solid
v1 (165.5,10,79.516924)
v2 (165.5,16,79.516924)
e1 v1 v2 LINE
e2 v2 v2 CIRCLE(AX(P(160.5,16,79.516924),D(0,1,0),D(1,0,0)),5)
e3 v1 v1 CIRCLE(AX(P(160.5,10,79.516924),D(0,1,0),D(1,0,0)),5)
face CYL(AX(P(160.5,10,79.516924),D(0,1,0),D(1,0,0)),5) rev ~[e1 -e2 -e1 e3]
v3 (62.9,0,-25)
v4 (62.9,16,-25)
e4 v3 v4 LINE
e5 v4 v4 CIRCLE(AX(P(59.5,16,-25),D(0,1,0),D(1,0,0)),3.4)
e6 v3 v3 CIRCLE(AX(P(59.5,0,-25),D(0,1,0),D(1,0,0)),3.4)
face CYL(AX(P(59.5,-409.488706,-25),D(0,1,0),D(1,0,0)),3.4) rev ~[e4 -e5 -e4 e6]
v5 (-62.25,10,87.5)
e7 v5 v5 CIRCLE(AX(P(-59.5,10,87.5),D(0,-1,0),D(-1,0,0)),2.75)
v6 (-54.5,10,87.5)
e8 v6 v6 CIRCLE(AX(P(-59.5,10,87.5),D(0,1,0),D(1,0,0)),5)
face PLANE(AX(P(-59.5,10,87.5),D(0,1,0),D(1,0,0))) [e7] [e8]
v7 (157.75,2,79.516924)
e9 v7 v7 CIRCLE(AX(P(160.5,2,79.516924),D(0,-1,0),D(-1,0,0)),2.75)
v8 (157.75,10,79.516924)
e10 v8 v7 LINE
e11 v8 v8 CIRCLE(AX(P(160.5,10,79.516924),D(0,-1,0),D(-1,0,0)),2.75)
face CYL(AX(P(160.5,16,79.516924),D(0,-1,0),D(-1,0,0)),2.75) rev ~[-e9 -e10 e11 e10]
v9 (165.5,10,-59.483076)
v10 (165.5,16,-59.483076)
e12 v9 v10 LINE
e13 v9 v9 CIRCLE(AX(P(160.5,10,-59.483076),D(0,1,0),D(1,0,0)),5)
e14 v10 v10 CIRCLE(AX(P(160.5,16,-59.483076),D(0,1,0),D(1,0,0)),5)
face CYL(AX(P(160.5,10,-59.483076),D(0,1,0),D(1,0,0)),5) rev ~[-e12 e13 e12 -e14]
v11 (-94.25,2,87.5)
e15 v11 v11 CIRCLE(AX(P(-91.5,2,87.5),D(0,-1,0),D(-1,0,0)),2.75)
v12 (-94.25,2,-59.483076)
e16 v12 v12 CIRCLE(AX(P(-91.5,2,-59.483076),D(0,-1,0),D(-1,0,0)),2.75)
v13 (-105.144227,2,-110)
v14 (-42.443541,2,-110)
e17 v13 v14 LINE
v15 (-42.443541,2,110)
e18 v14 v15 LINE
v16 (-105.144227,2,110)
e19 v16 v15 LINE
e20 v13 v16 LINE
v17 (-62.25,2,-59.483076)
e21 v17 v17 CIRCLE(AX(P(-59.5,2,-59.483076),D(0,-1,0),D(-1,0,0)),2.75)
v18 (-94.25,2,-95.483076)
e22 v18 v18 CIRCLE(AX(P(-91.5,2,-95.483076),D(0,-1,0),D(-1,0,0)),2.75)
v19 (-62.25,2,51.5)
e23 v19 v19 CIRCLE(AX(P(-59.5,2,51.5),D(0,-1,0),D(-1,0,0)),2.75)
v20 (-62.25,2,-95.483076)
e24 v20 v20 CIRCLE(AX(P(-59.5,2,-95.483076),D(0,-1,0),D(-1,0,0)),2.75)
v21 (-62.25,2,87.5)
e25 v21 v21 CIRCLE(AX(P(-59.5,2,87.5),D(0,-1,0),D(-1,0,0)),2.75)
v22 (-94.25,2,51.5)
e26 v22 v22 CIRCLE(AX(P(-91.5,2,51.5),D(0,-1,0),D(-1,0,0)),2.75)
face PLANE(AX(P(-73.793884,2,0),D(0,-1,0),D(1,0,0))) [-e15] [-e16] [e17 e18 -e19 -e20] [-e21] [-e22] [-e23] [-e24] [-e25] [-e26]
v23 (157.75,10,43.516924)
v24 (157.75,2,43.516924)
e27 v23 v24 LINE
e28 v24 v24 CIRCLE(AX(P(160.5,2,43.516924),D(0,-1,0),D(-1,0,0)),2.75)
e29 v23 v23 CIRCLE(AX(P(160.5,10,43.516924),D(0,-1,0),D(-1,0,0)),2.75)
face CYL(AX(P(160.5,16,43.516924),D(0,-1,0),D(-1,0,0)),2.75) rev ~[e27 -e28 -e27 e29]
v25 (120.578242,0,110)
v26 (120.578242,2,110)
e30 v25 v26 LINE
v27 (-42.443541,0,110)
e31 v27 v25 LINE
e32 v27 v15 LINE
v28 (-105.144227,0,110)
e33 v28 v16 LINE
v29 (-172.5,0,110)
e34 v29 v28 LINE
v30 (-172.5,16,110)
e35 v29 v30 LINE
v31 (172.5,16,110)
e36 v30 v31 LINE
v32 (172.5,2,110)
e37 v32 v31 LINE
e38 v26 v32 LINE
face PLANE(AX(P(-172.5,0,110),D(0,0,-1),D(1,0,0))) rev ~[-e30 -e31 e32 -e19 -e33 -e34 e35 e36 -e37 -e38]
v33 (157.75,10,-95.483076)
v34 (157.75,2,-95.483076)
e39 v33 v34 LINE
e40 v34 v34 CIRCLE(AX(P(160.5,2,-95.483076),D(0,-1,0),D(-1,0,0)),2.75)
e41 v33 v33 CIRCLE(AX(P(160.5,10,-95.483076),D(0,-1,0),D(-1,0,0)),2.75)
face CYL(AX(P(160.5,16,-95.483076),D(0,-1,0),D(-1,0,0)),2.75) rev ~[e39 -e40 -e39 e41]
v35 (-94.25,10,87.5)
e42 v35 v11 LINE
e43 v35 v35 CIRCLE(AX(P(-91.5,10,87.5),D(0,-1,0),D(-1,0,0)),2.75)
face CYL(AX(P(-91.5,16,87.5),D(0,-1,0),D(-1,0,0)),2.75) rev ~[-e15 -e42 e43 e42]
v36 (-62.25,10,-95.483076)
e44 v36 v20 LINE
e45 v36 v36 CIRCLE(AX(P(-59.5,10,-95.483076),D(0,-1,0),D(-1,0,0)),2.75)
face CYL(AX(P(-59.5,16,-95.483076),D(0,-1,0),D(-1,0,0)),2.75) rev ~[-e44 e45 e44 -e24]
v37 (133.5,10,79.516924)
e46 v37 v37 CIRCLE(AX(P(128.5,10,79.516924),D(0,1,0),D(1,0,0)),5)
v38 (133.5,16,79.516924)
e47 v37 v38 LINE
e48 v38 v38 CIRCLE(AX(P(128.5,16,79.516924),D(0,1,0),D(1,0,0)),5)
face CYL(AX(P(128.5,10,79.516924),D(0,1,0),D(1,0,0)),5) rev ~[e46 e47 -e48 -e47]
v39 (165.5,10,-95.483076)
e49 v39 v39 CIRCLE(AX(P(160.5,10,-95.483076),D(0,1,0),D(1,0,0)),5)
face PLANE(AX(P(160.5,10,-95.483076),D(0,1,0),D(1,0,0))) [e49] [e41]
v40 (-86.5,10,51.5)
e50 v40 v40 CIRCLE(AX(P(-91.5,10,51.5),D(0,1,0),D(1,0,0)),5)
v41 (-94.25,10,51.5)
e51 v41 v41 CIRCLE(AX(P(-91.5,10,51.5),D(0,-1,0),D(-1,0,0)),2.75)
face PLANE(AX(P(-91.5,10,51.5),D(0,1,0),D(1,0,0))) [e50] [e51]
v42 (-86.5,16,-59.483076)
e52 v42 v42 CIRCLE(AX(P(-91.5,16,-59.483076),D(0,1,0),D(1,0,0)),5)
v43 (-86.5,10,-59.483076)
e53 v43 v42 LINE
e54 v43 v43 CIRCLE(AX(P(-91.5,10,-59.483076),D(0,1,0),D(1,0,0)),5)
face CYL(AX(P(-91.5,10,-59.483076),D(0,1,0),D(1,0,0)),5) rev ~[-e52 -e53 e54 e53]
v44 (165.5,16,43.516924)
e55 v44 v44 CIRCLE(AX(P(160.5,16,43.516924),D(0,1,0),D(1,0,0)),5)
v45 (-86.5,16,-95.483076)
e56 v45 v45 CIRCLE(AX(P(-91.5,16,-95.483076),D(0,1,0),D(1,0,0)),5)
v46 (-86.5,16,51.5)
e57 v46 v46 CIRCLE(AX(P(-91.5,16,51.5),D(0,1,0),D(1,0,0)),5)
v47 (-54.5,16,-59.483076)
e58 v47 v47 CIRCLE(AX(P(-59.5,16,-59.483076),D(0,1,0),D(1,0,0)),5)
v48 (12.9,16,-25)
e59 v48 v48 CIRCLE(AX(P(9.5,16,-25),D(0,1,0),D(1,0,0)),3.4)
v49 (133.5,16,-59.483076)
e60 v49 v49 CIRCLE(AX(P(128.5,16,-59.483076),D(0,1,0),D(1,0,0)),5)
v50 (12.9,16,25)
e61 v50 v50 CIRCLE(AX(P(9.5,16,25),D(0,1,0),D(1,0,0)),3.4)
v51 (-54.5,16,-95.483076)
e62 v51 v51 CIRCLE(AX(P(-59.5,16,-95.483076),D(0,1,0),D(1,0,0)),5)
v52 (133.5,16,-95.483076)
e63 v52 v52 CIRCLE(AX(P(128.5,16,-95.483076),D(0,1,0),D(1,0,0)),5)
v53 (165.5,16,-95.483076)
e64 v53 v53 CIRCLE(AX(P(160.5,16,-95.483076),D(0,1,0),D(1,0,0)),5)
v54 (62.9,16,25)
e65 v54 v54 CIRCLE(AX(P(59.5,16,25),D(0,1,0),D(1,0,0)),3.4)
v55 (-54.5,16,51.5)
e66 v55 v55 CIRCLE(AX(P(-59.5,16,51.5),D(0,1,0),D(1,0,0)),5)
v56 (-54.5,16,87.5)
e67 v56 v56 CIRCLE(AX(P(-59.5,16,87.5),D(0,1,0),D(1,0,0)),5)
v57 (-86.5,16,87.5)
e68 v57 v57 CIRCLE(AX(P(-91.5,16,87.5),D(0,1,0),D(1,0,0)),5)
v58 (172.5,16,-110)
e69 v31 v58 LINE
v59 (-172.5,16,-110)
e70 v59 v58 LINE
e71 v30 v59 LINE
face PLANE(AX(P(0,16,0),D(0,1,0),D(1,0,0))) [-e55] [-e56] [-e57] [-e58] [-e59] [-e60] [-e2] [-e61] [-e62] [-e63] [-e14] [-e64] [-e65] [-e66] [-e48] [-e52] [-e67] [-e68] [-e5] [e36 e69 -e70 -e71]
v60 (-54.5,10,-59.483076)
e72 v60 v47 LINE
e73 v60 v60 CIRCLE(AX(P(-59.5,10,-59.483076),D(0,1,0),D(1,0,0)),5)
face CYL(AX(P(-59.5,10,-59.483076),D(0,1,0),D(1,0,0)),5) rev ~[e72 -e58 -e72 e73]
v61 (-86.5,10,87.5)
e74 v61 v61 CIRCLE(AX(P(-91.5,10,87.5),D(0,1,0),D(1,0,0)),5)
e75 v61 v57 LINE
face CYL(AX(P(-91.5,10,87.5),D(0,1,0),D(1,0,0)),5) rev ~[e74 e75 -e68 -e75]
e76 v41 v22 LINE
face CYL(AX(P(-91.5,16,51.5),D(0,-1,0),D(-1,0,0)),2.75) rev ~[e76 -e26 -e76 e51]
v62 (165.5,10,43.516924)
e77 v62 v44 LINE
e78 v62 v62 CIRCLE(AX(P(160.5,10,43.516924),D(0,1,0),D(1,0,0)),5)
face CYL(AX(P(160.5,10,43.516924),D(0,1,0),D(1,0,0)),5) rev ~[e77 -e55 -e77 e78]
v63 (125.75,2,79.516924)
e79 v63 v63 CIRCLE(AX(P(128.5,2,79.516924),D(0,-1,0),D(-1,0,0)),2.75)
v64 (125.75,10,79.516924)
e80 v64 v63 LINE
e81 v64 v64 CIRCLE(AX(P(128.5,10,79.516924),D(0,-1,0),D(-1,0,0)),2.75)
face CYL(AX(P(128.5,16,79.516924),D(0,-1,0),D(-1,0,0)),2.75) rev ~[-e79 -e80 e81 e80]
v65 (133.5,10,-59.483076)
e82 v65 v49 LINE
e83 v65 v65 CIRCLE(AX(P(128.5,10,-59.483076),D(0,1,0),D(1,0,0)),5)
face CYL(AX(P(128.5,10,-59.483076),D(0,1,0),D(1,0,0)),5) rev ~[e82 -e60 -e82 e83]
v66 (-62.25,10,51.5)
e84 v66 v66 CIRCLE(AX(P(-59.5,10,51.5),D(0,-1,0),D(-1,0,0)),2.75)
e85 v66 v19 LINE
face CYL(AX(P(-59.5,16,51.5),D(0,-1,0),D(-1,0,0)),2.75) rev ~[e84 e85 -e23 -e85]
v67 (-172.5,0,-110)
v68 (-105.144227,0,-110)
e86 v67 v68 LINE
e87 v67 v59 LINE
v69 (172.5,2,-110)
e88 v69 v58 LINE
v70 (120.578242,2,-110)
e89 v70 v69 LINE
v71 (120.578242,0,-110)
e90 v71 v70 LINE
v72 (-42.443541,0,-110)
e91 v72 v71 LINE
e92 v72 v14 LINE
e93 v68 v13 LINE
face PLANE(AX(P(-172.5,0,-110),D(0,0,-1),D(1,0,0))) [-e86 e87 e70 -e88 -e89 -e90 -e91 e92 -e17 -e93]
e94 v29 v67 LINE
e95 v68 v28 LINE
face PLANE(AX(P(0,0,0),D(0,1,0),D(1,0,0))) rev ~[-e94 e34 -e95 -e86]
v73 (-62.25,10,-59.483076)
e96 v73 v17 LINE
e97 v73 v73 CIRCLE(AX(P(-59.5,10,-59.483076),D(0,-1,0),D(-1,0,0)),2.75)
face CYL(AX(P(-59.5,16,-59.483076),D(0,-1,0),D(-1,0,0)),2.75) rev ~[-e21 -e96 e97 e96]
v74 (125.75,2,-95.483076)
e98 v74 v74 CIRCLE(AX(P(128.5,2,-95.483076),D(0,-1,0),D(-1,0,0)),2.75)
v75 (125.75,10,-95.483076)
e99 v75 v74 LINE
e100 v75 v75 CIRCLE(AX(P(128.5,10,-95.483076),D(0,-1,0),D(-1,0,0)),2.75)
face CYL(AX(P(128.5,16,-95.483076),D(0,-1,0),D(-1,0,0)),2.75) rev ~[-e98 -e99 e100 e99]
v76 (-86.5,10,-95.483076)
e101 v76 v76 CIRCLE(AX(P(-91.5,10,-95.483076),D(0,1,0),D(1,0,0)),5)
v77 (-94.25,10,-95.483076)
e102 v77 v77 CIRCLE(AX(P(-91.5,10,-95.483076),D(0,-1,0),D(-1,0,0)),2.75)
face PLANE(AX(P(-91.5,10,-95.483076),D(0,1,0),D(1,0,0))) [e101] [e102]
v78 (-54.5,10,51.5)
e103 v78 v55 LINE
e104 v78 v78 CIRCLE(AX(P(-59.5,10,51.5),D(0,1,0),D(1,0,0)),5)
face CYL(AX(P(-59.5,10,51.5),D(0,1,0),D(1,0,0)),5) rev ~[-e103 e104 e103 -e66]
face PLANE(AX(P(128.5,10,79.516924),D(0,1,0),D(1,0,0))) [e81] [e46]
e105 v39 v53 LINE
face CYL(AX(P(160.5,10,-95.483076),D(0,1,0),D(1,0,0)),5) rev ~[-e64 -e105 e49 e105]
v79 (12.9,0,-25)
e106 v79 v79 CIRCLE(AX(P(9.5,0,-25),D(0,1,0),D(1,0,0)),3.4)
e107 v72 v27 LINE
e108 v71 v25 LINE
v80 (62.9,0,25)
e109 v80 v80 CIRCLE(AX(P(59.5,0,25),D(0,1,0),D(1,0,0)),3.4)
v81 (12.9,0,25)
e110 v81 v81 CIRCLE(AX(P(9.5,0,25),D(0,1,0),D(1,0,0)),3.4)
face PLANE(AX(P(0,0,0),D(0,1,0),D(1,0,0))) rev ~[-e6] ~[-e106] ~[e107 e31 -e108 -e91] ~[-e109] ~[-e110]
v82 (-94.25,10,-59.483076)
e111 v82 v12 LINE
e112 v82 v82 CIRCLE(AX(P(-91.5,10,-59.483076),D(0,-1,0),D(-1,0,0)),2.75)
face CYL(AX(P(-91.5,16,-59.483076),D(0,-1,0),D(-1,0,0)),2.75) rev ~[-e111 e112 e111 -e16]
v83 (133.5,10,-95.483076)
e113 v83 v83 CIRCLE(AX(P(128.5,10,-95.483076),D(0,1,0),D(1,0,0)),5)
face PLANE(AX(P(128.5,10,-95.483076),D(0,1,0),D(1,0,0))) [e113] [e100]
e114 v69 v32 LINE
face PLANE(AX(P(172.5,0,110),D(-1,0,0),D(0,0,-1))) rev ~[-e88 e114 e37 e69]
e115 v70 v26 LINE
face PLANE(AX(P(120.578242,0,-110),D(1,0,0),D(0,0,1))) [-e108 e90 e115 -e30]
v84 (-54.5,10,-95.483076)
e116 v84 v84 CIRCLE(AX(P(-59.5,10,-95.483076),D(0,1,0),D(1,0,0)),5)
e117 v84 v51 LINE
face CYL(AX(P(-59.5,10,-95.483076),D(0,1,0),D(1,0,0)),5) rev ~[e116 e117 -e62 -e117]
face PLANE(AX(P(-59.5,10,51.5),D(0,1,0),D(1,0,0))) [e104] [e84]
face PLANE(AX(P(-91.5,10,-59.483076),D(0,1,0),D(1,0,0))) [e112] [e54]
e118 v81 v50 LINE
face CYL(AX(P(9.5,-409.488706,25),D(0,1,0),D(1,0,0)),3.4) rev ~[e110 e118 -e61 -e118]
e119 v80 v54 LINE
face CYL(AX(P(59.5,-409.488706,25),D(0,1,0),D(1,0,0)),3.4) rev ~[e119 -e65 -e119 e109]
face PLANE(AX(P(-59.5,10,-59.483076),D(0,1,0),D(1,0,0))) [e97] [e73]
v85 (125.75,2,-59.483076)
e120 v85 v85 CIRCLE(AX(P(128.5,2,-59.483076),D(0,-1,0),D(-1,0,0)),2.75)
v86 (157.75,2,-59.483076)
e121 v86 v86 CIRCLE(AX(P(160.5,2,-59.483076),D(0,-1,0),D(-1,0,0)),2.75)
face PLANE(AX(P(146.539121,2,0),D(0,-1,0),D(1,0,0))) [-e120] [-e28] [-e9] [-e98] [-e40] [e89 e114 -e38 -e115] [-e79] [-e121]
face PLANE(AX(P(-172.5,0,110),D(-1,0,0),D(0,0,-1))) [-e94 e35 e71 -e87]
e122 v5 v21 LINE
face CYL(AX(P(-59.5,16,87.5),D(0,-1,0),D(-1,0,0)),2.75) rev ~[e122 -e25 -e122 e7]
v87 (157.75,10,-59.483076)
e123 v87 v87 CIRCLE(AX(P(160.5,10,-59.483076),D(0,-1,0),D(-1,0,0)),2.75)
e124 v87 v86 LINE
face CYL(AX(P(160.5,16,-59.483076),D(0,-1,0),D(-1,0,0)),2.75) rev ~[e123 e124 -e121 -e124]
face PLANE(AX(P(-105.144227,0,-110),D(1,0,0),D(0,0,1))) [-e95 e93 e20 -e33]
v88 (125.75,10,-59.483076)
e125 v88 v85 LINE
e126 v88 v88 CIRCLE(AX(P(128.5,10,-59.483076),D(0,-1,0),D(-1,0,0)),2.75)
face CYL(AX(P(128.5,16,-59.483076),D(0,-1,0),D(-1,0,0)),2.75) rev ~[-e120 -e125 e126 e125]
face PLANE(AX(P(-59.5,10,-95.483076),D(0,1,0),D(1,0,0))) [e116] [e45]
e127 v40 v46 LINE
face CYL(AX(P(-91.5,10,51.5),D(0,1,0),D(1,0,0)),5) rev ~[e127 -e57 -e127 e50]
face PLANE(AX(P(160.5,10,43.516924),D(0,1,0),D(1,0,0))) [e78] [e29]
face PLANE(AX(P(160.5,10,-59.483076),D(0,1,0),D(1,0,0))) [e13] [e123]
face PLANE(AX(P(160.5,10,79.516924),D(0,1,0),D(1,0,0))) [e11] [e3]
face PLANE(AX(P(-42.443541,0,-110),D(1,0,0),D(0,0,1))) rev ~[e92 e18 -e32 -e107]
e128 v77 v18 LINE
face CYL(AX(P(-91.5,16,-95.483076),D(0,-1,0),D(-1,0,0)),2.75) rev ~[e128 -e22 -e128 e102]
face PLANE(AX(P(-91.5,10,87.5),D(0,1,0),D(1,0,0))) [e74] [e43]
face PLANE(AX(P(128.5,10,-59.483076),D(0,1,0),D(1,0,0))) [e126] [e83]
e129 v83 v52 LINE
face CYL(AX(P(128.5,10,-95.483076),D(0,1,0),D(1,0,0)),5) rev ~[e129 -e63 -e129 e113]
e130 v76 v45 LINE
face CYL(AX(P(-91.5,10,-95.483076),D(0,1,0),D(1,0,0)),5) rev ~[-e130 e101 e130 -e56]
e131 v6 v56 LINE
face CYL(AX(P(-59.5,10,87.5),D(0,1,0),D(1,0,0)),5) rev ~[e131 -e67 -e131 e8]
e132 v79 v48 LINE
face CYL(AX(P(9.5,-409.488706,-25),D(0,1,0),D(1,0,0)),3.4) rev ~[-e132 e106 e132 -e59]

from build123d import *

# Parameters (mm, degrees)
SKETCH1_W                               = 345
SKETCH1_H                               = 220
BOSS_EXTRUDE1_DEPTH                     = 16
CBORE_FOR_M5_HEX_HEAD_BOLT1_D           = 5.5
CBORE_FOR_M5_HEX_HEAD_BOLT1_CBORE_D     = 10
CBORE_FOR_M5_HEX_HEAD_BOLT1_CBORE_DEPTH = 6
SKETCH4_W                               = 62.700686025
SKETCH4_H                               = 220
SKETCH4_W_2                             = 51.921757643
CUT_EXTRUDE1_DEPTH                      = 2
M8_TAPPED_HOLE1_D                       = 6.8


with BuildPart() as part:
    # Sketch1 → Boss-Extrude1 (new body)
    with BuildSketch(Plane(origin=(0, 0, 0), x_dir=(1, 0, 0), z_dir=(0, 1, 0))):
        Rectangle(SKETCH1_W, SKETCH1_H)
    extrude(amount=BOSS_EXTRUDE1_DEPTH)

    # CBORE for M5 Hex Head Bolt1 (through all)
    with Locations(Plane(origin=(0, 16, 0), x_dir=(1, 0, 0), z_dir=(0, 1, 0))):
        with Locations((160.5, 95.483075679), (128.5, 95.483075679), (128.5, 59.483075679), (160.5, 59.483075679), (160.5, -43.516924321), (160.5, -79.516924321), (128.5, -79.516924321), (-91.5, -51.5), (-59.5, -51.5), (-59.5, -87.5), (-91.5, -87.5), (-91.5, 59.483075679), (-59.5, 59.483075679), (-59.5, 95.483075679), (-91.5, 95.483075679)):
            CounterBoreHole(CBORE_FOR_M5_HEX_HEAD_BOLT1_D / 2, CBORE_FOR_M5_HEX_HEAD_BOLT1_CBORE_D / 2, CBORE_FOR_M5_HEX_HEAD_BOLT1_CBORE_DEPTH)

    # Sketch4 → Cut-Extrude1 (cut)
    with BuildSketch(Plane.XZ):
        with Locations((-73.793884323, 0)):
            Rectangle(SKETCH4_W, SKETCH4_H)
        with Locations((146.539121179, 0)):
            Rectangle(SKETCH4_W_2, SKETCH4_H)
    extrude(amount=-CUT_EXTRUDE1_DEPTH, mode=Mode.SUBTRACT)

    # M8 Tapped Hole1 (through all)
    with Locations(Plane(origin=(0, 0, 0), x_dir=(-1, 0, 0), z_dir=(0, -1, 0))):
        with Locations((-59.5, 25), (-9.5, 25), (-9.5, -25), (-59.5, -25)):
            Hole(M8_TAPPED_HOLE1_D / 2)


solid = part.part
